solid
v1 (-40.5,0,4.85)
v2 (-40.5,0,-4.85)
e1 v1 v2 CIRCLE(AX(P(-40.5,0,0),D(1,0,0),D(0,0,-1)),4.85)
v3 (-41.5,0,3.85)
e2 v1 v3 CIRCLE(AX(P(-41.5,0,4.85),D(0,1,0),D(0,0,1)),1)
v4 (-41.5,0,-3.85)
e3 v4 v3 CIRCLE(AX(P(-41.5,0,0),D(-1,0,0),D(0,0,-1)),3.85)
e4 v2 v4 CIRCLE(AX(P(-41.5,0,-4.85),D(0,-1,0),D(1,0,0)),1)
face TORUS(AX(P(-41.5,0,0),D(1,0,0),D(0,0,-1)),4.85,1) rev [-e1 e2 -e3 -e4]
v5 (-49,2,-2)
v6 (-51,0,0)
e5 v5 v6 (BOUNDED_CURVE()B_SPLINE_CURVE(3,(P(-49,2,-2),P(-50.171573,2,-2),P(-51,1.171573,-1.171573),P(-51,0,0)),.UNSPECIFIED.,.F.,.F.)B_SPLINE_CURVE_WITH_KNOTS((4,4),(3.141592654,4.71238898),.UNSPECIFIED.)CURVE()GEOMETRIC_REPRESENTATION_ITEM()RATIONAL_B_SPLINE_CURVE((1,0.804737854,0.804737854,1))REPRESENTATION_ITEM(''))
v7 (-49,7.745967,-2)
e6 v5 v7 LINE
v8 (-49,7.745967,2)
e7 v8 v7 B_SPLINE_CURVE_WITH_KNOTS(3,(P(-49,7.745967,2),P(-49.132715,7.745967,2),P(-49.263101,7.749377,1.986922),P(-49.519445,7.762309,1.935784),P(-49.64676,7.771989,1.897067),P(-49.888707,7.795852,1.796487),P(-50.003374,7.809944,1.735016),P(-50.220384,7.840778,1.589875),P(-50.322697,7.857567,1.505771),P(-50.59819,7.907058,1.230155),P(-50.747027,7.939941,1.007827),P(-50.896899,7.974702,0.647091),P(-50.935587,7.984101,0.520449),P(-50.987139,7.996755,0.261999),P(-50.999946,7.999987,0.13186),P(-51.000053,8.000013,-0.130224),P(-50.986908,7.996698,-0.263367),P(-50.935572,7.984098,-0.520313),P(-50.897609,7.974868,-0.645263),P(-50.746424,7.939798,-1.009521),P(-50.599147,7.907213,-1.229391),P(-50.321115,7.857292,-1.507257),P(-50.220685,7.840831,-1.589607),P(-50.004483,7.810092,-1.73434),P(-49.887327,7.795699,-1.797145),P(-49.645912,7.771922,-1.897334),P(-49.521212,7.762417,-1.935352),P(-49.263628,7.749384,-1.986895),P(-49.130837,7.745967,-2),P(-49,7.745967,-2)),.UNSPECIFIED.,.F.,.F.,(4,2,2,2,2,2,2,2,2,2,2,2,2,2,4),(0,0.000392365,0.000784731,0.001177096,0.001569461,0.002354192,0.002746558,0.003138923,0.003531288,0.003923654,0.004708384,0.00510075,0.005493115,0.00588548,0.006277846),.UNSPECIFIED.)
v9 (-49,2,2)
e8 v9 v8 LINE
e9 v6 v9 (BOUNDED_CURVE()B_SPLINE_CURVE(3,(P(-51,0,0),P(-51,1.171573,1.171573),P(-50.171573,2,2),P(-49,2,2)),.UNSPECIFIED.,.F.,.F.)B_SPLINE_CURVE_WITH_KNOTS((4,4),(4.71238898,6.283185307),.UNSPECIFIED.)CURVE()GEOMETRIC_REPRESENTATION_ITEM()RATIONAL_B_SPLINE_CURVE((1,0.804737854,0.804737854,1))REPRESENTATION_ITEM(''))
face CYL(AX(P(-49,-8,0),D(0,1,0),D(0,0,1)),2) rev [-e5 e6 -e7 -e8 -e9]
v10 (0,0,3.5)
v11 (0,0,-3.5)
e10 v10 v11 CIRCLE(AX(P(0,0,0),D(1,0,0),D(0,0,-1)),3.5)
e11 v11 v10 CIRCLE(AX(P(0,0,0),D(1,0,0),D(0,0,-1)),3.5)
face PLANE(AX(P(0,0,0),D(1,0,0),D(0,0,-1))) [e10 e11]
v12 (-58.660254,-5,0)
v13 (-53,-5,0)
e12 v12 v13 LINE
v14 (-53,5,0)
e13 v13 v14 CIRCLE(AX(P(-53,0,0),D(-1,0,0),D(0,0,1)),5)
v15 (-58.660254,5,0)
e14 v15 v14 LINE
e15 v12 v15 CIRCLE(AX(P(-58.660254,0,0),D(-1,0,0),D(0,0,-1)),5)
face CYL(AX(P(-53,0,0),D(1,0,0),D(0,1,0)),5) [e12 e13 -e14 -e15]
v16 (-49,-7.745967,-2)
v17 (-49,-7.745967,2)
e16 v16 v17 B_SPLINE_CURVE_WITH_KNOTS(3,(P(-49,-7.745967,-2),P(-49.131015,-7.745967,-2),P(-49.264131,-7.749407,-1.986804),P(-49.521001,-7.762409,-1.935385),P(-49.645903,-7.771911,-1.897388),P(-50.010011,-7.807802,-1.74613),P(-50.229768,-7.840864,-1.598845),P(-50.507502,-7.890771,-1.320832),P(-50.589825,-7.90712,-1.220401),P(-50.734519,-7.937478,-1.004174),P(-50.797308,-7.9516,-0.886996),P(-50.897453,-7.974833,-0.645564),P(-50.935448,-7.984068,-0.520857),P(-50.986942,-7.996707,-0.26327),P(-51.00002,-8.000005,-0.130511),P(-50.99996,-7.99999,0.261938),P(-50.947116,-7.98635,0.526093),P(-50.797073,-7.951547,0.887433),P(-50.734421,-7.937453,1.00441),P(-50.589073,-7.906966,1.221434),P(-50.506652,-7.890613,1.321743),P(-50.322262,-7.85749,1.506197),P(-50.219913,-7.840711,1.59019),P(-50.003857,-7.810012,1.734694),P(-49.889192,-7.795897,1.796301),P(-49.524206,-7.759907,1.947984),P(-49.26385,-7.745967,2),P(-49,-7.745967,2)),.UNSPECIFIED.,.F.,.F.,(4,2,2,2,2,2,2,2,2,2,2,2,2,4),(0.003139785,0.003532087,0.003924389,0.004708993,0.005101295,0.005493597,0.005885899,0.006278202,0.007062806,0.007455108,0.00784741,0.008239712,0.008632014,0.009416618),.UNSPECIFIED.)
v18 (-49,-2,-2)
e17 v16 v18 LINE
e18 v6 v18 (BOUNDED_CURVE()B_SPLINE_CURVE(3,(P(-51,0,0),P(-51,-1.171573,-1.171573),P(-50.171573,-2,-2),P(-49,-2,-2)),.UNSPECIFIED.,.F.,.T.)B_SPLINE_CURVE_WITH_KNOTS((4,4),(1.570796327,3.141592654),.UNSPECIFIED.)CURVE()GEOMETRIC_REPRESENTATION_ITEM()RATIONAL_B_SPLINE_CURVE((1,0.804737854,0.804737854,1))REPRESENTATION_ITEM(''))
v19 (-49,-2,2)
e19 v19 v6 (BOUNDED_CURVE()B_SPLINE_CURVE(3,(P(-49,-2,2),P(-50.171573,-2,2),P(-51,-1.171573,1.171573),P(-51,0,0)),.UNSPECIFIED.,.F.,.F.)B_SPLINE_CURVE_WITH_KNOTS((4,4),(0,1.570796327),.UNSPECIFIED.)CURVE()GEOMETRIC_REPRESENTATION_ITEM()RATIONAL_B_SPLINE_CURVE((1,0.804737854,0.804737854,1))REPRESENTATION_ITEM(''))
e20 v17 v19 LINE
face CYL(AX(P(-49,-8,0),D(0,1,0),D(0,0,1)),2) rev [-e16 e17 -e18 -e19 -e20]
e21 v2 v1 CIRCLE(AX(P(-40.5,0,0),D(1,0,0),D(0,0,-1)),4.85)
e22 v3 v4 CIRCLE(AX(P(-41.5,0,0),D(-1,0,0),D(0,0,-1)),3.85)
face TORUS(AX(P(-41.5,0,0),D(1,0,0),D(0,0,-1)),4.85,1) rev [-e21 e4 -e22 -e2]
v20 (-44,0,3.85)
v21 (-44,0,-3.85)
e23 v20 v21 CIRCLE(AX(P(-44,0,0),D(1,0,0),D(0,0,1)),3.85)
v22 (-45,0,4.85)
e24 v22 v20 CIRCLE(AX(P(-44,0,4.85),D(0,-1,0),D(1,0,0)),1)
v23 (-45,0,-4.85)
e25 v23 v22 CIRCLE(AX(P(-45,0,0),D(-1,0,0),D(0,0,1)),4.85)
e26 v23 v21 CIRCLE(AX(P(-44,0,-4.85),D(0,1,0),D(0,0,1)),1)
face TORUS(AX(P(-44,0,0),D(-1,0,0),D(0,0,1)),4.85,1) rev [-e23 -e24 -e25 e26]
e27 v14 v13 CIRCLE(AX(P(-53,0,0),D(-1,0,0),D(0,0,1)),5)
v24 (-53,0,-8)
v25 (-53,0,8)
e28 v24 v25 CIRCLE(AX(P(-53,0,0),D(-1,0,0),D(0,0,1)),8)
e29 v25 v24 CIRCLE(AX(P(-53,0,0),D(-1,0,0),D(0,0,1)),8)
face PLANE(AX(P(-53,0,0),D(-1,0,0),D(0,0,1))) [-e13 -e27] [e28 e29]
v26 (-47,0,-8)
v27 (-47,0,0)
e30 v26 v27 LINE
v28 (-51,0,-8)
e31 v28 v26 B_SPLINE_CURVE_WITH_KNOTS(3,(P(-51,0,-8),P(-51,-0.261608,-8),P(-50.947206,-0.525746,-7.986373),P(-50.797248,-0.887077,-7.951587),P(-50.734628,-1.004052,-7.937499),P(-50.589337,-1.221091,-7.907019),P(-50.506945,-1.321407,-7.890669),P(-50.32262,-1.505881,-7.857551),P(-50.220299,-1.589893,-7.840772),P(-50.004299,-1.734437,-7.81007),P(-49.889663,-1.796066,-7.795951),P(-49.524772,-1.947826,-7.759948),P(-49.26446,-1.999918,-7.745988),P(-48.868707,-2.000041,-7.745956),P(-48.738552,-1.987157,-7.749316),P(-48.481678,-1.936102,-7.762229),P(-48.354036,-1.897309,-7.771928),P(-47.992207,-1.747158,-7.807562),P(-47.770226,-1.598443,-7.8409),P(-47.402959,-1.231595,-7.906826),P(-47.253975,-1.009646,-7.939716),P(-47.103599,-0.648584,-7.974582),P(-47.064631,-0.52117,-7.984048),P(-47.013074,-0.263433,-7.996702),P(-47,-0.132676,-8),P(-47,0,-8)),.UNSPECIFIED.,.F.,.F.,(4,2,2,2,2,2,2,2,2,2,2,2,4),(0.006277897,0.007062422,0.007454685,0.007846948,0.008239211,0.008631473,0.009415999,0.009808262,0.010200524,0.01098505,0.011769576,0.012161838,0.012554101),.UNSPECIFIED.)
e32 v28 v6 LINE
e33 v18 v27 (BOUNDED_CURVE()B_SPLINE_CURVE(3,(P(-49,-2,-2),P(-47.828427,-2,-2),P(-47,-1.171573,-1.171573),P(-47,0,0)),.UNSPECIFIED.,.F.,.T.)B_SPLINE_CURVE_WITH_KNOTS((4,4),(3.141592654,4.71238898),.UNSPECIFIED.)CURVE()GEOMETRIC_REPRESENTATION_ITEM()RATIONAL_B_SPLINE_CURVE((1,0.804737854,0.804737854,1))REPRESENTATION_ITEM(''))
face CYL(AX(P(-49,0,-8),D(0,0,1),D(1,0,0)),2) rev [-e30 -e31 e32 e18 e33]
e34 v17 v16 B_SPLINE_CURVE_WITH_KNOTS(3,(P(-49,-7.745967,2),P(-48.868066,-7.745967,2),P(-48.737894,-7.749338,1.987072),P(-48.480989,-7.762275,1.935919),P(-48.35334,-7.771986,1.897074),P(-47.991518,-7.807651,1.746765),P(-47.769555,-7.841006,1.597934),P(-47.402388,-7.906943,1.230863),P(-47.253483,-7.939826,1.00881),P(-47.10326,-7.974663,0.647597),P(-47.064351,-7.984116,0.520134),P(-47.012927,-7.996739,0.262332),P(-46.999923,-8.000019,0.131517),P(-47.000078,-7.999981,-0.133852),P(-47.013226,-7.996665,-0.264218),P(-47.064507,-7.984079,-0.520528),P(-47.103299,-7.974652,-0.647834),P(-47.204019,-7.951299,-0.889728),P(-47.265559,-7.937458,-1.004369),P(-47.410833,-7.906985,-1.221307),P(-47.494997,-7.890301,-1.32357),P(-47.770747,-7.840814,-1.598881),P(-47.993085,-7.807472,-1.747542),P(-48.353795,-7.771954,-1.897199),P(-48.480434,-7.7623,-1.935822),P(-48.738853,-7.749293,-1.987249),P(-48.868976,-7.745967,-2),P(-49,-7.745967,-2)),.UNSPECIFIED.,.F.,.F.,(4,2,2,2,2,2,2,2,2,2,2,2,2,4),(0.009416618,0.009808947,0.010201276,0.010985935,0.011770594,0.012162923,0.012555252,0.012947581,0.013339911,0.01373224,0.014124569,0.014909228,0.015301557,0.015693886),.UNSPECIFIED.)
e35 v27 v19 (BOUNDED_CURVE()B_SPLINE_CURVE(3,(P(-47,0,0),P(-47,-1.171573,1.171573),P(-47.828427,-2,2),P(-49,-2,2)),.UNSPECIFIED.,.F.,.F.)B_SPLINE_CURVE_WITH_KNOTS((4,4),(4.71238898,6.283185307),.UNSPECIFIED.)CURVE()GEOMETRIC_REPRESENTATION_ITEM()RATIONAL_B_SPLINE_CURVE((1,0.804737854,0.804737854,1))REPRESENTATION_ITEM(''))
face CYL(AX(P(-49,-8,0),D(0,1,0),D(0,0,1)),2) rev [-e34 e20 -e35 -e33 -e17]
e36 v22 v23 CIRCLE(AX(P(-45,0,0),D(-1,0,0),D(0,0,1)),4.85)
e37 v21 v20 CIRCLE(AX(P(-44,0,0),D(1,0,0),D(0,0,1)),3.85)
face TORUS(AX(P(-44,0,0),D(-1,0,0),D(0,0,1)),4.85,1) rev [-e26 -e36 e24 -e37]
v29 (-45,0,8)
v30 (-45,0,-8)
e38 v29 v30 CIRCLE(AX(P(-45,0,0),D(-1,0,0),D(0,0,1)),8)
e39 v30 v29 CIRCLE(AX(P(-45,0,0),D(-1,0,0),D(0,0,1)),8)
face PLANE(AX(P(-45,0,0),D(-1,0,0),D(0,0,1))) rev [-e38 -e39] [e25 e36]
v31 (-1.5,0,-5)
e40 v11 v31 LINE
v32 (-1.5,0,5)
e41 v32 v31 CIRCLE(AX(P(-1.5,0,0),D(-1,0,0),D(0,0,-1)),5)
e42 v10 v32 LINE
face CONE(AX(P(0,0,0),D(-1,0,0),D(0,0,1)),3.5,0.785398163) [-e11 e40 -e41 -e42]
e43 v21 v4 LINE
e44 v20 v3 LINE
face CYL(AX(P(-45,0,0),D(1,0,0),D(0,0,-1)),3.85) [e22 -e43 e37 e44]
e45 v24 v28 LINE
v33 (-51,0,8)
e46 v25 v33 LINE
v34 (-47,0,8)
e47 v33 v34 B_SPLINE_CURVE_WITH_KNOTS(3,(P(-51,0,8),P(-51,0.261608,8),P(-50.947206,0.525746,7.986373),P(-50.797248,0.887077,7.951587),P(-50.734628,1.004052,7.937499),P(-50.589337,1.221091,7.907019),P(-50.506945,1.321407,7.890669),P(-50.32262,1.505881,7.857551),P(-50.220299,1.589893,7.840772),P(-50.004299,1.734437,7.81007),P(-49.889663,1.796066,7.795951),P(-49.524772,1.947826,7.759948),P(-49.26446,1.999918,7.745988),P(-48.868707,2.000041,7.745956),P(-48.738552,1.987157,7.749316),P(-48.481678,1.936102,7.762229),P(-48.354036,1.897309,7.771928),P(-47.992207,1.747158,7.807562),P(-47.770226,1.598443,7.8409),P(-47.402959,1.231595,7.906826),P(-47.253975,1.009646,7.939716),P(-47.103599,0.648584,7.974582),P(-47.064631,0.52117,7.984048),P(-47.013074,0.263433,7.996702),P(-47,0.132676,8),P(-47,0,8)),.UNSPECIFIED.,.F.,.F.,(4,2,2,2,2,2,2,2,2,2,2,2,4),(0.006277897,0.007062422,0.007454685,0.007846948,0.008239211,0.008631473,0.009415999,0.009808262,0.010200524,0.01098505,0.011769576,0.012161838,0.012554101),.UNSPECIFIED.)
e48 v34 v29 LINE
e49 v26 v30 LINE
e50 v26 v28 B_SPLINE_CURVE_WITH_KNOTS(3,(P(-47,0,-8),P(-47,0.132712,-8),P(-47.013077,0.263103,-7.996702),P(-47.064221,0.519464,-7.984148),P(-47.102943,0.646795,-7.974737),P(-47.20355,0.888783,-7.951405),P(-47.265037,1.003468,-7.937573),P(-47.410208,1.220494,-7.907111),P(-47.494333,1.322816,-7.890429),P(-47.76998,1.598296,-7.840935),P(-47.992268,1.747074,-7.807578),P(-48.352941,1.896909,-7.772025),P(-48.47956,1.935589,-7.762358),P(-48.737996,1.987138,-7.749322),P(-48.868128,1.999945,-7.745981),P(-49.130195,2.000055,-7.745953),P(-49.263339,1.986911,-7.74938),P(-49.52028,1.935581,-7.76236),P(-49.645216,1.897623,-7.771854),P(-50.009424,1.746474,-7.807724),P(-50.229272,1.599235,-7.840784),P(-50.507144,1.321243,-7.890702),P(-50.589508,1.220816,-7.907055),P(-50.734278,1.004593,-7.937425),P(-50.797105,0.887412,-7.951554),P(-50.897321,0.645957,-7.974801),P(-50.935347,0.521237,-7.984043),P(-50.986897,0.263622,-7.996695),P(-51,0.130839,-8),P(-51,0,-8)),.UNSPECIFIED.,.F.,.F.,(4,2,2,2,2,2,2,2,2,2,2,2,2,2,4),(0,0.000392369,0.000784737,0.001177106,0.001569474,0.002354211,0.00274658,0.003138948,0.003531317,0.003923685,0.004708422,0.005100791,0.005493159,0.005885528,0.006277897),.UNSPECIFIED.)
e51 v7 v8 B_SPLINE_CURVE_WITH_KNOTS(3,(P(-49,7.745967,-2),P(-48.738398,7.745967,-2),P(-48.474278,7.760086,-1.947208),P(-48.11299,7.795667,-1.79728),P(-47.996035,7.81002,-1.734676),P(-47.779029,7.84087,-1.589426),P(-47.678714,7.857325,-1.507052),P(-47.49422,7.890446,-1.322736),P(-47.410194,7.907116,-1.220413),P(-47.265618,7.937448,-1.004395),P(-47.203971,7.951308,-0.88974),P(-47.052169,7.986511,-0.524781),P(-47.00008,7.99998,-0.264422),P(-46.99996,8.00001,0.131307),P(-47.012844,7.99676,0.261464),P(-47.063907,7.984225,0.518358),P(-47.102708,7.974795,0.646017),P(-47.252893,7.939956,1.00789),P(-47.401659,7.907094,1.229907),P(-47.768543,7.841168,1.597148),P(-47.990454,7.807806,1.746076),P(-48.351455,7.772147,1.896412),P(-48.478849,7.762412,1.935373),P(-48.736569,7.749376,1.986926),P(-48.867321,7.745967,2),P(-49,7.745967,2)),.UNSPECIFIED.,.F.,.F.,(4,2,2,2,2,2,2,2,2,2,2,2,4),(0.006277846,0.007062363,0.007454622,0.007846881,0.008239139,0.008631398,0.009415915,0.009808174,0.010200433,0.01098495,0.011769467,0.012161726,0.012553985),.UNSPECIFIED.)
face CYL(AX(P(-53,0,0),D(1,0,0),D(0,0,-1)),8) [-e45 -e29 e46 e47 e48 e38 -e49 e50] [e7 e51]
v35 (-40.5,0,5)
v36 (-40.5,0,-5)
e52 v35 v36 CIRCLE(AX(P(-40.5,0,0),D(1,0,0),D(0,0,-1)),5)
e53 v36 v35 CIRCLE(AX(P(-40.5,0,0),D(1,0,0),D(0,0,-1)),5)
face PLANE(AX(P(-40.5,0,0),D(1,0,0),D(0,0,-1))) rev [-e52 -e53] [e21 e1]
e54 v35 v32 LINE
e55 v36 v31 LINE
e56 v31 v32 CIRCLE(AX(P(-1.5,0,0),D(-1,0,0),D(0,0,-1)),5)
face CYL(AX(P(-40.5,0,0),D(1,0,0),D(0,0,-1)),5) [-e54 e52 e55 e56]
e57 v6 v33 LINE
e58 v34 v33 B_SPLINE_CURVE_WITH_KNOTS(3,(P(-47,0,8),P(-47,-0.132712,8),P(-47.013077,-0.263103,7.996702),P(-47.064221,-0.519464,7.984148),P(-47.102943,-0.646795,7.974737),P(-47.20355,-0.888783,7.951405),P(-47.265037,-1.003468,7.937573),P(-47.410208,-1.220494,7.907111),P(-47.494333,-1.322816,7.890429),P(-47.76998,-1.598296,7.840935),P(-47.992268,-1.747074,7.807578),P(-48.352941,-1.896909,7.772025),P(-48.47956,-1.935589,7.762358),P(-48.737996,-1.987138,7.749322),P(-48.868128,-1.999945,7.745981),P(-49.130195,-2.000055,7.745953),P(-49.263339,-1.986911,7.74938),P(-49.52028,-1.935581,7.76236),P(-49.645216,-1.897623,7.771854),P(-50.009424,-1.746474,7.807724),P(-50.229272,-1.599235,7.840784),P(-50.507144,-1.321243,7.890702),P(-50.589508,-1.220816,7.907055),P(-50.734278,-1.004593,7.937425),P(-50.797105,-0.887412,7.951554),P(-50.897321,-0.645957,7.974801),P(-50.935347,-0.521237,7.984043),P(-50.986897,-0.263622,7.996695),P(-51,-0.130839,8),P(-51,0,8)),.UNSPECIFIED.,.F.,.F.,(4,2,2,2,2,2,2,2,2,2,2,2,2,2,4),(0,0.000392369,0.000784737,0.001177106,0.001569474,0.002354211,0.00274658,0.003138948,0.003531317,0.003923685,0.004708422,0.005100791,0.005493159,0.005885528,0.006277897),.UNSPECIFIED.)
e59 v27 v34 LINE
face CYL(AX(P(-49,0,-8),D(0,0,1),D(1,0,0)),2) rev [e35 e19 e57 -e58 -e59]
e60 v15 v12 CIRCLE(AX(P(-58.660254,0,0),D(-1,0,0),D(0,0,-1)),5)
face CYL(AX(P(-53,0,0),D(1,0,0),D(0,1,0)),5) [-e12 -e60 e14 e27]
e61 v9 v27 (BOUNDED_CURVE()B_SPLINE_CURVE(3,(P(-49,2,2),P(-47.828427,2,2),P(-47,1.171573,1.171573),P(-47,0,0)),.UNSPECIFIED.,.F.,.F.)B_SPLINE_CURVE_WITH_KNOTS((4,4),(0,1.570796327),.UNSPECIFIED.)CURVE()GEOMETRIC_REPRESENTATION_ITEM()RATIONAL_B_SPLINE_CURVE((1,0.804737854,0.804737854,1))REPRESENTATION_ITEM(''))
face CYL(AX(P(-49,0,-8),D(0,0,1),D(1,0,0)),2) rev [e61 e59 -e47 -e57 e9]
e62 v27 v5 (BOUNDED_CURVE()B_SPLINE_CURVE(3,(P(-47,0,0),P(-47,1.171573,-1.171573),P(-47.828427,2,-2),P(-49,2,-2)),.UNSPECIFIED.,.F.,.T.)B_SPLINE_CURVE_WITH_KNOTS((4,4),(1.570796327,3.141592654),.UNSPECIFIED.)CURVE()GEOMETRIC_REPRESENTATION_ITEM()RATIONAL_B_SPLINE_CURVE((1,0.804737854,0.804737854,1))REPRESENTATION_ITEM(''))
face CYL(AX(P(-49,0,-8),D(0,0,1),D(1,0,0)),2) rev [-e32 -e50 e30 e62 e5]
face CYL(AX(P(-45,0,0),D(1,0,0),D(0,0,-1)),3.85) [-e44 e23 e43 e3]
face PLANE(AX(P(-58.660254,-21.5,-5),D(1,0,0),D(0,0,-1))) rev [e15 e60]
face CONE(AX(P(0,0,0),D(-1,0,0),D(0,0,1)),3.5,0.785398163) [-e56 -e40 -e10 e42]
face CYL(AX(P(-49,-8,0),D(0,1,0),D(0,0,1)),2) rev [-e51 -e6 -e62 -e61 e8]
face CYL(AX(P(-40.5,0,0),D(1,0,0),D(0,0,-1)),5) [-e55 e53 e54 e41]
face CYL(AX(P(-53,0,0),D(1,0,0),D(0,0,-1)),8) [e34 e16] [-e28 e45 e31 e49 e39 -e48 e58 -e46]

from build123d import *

# Parameters (mm, degrees)
SKETCH1_R               = 5
BOSS_EXTRUDE_DEPTH      = 40.5
CHAMFER2_SIZE           = 1.5
SKETCH2_R               = 3.85
BOSS_EXTRUDE1_DEPTH     = 4.5
SKETCH4_R               = 8
BOSS_EXTRUDE2_DEPTH     = 8
CUT_EXTRUDE1_DEPTH      = 55.194095619
CUT_EXTRUDE1_DEPTH_BACK = 55.194095619
SKETCH6_R               = 2
CUT_EXTRUDE2_DEPTH      = 55.194095747
CUT_EXTRUDE2_DEPTH_BACK = 55.194095747
SKETCH7_R               = 2
FILLET1_R               = 1
SKETCH15_W              = 10.32482264
SKETCH15_H              = 14.834361989
CUT_EXTRUDE3_DEPTH      = 21.5


with BuildPart() as part:
    # Sketch1 → Boss-Extrude (new body)
    with BuildSketch(Plane(origin=(0, 0, 0), x_dir=(0, 0, -1), z_dir=(1, 0, 0))):
        Circle(SKETCH1_R)
    extrude(amount=-BOSS_EXTRUDE_DEPTH)

    # Chamfer2
    chamfer2_edges = [part.edges().sort_by_distance(p)[0] for p in [
        (0, 0, 5),
    ]]
    chamfer(chamfer2_edges, length=CHAMFER2_SIZE)

    # Sketch2 → Boss-Extrude1 (add)
    with BuildSketch(Plane.ZY.offset(40.5)):
        with Locations(Location((0, 0, 0), (0, 0, 180))):
            Circle(SKETCH2_R)
    extrude(amount=BOSS_EXTRUDE1_DEPTH)

    # Sketch4 → Boss-Extrude2 (add)
    with BuildSketch(Plane.ZY.offset(45)):
        Circle(SKETCH4_R)
    extrude(amount=BOSS_EXTRUDE2_DEPTH)

    # Sketch6 → Cut-Extrude1 (cut, two sides: drawn at the far end of the back side and taken through both)
    with BuildSketch(Plane.XY.offset(-CUT_EXTRUDE1_DEPTH_BACK)):
        with Locations((-49, 0)):
            Circle(SKETCH6_R)
    extrude(amount=CUT_EXTRUDE1_DEPTH + CUT_EXTRUDE1_DEPTH_BACK, mode=Mode.SUBTRACT)

    # Sketch7 → Cut-Extrude2 (cut, two sides: drawn at the far end of the back side and taken through both)
    with BuildSketch(Plane(origin=(0, 0, 0), x_dir=(1, 0, 0), z_dir=(0, 1, 0)).offset(-CUT_EXTRUDE2_DEPTH_BACK)):
        with Locations(Location((-49, 0, 0), (0, 0, 270))):
            Circle(SKETCH7_R)
    extrude(amount=CUT_EXTRUDE2_DEPTH + CUT_EXTRUDE2_DEPTH_BACK, mode=Mode.SUBTRACT)

    # Sketch14 → Boss-Revolve1 (revolve)
    with BuildSketch(Plane.XY):
        with BuildLine():
            Line((-53, 0), (-53, 5))
            Line((-53, 5), (-58.660254038, 5))
            ThreePointArc((-58.660254038, 5), (-59.659258263, 2.588190451), (-60, 0))
            Line((-60, 0), (-53, 0))
        make_face()
    revolve(axis=Axis((-53, 0, 0), (-1, 0, 0)))

    # Fillet1
    fillet1_edges = [part.edges().sort_by_distance(p)[0] for p in [
        (-40.5, 0, 3.85),
        (-45, 0, 3.85),
    ]]
    fillet(fillet1_edges, radius=FILLET1_R)

    # Sketch15 → Cut-Extrude3 (cut, symmetric)
    with BuildSketch(Plane(origin=(0, 0, 0), x_dir=(1, 0, 0), z_dir=(0, 1, 0))):
        with Locations((-63.822665358, -2.417180995)):
            Rectangle(SKETCH15_W, SKETCH15_H)
    extrude(amount=CUT_EXTRUDE3_DEPTH, both=True, mode=Mode.SUBTRACT)


solid = part.part
